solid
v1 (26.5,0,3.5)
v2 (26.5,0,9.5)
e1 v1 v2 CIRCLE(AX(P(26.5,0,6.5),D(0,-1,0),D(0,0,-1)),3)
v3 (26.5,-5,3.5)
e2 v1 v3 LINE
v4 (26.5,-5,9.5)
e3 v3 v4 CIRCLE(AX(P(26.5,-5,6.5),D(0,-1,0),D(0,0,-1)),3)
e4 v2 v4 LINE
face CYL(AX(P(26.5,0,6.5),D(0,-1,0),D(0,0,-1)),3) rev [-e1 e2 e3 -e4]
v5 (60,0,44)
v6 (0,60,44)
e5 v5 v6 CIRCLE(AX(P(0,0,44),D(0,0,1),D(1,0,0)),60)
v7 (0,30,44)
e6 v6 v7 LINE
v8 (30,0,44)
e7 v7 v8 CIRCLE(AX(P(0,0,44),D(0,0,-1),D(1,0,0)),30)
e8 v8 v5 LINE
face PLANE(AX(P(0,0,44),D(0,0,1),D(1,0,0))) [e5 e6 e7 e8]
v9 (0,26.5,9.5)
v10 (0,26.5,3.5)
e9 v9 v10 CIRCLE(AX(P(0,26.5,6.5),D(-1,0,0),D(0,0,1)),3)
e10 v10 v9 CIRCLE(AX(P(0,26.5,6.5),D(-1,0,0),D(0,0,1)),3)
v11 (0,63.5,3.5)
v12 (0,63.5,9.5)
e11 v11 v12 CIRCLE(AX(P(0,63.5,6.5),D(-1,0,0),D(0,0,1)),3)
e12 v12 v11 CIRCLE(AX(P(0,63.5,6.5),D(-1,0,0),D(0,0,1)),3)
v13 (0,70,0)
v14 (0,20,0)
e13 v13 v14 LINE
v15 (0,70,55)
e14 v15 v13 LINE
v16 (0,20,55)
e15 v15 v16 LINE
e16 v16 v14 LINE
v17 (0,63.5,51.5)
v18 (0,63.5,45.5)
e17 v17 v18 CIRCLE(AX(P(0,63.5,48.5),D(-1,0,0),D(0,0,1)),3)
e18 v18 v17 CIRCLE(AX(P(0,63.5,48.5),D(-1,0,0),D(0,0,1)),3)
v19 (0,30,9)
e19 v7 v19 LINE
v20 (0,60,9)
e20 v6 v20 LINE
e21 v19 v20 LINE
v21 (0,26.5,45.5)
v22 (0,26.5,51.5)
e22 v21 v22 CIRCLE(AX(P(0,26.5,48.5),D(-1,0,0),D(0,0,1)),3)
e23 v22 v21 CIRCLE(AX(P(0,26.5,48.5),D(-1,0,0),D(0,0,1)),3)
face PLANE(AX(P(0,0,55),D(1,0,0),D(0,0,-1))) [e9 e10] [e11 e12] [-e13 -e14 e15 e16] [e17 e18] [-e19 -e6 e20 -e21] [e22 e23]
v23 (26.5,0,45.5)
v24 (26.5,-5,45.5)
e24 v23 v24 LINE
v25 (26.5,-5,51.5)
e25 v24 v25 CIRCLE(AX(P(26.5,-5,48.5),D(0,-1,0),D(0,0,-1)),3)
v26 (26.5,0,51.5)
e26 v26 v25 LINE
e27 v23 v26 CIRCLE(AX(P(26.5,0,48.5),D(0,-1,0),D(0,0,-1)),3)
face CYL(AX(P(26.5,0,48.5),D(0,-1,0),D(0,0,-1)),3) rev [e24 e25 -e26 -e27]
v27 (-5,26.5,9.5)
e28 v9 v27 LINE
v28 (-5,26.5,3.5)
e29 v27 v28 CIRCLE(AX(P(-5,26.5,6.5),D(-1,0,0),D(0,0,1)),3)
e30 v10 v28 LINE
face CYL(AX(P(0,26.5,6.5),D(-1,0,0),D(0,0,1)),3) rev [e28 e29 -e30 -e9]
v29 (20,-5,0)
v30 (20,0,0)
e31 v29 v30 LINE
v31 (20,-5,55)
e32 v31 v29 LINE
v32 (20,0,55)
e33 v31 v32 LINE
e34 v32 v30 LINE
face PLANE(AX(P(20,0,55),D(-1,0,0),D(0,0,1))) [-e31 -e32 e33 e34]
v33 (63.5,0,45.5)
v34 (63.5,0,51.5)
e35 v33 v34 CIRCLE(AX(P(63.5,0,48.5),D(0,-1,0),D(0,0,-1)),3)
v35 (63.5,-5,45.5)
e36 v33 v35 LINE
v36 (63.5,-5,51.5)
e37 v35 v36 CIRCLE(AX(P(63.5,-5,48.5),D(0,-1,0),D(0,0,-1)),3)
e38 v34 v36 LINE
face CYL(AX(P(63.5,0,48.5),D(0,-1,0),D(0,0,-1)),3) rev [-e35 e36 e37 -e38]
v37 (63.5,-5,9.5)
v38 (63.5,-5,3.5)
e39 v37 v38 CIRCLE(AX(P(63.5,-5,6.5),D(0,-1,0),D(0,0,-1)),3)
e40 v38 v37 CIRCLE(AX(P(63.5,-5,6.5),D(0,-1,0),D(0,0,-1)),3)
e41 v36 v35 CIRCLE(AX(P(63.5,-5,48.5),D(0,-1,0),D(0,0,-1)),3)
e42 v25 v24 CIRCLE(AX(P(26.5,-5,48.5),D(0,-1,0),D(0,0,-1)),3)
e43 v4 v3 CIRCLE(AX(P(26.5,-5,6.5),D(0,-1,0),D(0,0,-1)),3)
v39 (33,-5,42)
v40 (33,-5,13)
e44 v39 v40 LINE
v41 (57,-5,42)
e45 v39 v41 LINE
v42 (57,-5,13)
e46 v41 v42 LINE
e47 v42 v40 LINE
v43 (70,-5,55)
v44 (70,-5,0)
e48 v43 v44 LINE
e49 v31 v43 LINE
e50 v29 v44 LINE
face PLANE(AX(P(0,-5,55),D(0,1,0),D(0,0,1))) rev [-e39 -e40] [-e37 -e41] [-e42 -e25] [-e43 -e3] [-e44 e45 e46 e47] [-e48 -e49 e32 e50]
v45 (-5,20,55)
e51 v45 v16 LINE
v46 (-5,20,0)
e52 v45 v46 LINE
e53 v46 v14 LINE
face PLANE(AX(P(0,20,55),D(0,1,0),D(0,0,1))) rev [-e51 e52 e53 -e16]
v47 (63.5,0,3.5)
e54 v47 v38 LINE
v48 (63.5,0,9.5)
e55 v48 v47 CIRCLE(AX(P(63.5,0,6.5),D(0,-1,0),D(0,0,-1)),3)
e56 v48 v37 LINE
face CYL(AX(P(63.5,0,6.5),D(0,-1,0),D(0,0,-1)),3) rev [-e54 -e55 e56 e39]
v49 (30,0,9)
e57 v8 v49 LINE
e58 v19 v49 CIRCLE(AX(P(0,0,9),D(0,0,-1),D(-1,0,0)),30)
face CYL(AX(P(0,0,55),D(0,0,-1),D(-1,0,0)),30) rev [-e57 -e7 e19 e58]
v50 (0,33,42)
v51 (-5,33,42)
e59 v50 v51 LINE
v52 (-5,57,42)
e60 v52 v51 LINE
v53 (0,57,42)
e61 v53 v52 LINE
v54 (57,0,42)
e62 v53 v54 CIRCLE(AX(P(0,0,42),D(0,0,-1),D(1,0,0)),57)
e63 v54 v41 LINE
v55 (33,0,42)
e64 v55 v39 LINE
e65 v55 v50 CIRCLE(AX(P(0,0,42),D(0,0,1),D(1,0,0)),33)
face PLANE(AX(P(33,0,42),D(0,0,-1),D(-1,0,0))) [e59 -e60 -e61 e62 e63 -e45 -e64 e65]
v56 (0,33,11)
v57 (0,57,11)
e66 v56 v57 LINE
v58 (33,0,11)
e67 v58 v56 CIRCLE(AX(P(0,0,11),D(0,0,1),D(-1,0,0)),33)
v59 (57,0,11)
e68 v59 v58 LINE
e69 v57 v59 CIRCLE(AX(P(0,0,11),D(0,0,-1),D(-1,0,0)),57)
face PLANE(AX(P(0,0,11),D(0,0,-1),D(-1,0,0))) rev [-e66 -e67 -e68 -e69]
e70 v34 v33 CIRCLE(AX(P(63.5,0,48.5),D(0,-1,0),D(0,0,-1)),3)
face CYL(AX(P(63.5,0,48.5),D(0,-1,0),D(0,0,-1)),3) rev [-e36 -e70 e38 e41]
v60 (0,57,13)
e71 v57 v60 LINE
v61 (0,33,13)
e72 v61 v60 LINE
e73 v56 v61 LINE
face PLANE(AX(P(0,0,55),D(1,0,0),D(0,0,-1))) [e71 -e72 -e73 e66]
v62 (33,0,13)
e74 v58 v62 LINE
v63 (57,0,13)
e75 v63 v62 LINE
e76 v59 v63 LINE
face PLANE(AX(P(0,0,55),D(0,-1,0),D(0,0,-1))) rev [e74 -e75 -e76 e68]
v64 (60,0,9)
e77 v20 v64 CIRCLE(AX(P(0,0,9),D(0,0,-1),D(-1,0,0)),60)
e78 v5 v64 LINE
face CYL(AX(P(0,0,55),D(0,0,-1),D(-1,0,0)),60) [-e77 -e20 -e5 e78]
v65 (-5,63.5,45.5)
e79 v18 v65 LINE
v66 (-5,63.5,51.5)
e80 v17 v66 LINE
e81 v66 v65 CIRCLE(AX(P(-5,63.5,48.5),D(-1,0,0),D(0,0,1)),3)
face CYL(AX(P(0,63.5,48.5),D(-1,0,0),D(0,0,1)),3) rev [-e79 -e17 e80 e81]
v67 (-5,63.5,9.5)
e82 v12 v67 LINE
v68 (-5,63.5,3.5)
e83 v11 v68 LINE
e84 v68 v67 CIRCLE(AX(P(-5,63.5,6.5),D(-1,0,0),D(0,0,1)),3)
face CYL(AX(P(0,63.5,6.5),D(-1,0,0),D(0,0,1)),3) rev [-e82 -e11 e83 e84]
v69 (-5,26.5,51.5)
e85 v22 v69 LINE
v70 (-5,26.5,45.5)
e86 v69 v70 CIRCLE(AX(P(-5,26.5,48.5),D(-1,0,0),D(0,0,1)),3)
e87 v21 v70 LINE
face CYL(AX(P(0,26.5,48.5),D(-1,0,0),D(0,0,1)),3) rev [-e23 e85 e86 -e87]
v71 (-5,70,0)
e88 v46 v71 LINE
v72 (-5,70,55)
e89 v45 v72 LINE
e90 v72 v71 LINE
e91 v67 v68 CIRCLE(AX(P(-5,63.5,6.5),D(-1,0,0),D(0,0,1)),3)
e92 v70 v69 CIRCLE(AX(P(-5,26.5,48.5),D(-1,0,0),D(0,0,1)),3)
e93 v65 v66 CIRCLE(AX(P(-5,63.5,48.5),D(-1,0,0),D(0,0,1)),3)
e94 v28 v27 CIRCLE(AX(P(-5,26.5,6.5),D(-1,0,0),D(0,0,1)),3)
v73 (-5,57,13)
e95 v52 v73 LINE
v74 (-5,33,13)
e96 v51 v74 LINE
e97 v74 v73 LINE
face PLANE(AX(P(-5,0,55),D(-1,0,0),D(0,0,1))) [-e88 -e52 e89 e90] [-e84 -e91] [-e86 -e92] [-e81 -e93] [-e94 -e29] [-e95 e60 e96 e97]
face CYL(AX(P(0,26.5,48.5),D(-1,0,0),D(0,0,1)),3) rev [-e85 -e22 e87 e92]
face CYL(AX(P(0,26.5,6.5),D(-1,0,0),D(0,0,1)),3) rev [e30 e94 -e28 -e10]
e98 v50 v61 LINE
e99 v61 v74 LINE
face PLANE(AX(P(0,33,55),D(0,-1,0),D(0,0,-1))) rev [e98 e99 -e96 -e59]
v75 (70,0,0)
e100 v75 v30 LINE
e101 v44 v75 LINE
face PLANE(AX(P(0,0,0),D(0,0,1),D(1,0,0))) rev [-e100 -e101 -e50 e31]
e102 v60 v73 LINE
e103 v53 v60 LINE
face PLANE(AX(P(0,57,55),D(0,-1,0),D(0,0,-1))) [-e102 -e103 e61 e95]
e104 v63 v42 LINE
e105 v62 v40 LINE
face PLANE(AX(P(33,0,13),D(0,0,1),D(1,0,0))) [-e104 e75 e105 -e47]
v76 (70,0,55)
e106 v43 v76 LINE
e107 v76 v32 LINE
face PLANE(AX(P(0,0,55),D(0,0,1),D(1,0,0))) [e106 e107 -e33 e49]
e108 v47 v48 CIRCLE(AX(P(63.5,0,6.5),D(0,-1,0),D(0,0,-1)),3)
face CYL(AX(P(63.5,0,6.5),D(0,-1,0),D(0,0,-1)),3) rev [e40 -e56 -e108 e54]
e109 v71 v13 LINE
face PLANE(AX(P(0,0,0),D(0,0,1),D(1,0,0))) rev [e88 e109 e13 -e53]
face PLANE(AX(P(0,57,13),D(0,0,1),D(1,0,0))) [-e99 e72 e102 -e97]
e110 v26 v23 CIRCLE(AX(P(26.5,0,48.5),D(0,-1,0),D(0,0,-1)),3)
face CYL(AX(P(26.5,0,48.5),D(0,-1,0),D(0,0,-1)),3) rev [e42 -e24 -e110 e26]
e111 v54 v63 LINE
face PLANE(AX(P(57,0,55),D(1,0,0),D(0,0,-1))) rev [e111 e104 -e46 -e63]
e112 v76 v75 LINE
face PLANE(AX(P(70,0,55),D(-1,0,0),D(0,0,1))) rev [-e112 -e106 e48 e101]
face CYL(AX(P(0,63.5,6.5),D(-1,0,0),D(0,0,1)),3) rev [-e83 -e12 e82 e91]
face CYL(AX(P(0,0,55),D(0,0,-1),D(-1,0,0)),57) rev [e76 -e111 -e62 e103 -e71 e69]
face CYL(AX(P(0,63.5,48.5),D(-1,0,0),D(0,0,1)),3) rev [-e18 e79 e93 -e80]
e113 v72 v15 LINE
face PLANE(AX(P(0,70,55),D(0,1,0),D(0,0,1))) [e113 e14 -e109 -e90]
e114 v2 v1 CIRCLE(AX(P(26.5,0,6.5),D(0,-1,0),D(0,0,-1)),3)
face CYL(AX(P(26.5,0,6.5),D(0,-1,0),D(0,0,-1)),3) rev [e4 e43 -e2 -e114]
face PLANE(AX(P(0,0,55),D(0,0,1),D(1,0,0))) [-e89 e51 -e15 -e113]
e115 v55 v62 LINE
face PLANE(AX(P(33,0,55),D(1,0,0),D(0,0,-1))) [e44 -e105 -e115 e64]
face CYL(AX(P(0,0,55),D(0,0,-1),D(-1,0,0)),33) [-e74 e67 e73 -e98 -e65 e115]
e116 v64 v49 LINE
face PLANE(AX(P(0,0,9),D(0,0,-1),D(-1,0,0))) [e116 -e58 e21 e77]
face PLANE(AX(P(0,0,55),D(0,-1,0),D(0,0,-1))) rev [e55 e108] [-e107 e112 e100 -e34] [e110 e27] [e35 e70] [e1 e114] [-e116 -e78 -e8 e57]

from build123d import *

# Parameters (mm, degrees)
BEND_BODY_DEPTH               = 55
BEND_BODY_2_DEPTH             = 55
FLANGE_A_SKETCH_W             = 24
FLANGE_A_SKETCH_H             = 13
FLANGE_A_DEPTH                = 5
FLANGE_B_SKETCH_W             = 13
FLANGE_B_SKETCH_H             = 24
FLANGE_B_DEPTH                = 5
FLANGE_START                  = -15
FLANGE_B_TRANSITION_CUT_DEPTH = 15
FLANGE_A_TRANSITION_CUT_DEPTH = 15
FLANGE_START_2                = 2
FLANGE_A_PAD_1_DEPTH          = 2
FLANGE_B_PAD_1_DEPTH          = 2
FLANGE_B_PAD_2_DEPTH          = 2
FLANGE_START_3                = -2
FLANGE_B_PAD_3_DEPTH          = 2
FLANGE_A_PAD_2_DEPTH          = 2
FLANGE_A_PAD_3_DEPTH          = 2
FLANGE_A_PAD_4_DEPTH          = 2
BOLT_HOLES_SET_1_SKETCH_R     = 3
BOLT_HOLES_SET_1_4X_DEPTH     = 5
BOLT_HOLES_SET_2_SKETCH_R     = 3
BOLT_HOLES_SET_2_4X_DEPTH     = 5


with BuildPart() as part:
    # Bend Profile Sketch → Bend Body (new body)
    with BuildSketch(Plane.XY):
        with BuildLine():
            Line((0, 57), (-5, 57))
            Line((-5, 57), (-5, 70))
            Line((-5, 70), (0, 70))
            Line((0, 70), (0, 60))
            ThreePointArc((0, 60), (42.426406871, 42.426406871), (60, 0))
            Line((60, 0), (70, 0))
            Line((70, 0), (70, -5))
            Line((70, -5), (57, -5))
            Line((57, -5), (57, 0))
            ThreePointArc((57, 0), (40.305086528, 40.305086528), (0, 57))
        make_face()
    extrude(amount=BEND_BODY_DEPTH)



with BuildPart() as body_2:
    # Bend Profile Sketch → Bend Body 2 (new body)
    with BuildSketch(Plane.XY):
        with BuildLine():
            Line((0, 33), (-5, 33))
            Line((-5, 33), (-5, 20))
            Line((-5, 20), (0, 20))
            Line((0, 20), (0, 30))
            ThreePointArc((0, 30), (21.213203436, 21.213203436), (30, 0))
            Line((30, 0), (20, 0))
            Line((20, 0), (20, -5))
            Line((20, -5), (33, -5))
            Line((33, -5), (33, 0))
            ThreePointArc((33, 0), (23.334523779, 23.334523779), (0, 33))
        make_face()
    extrude(amount=BEND_BODY_2_DEPTH)


with BuildPart() as part_1:
    add(part.part)

    add(body_2.part)  # Flange A merges body 2
    # Flange A Sketch → Flange A (add)
    with BuildSketch(Plane(origin=(0, -5, 0), x_dir=(-1, 0, 0), z_dir=(0, -1, 0))):
        with Locations((-45, -48.5)):
            Rectangle(FLANGE_A_SKETCH_W, FLANGE_A_SKETCH_H)
        with Locations((-45, -6.5)):
            Rectangle(FLANGE_A_SKETCH_W, FLANGE_A_SKETCH_H)
    extrude(amount=-FLANGE_A_DEPTH)

    # Flange B Sketch → Flange B (add)
    with BuildSketch(Plane.ZY.offset(5)):
        with Locations((48.5, 45)):
            Rectangle(FLANGE_B_SKETCH_W, FLANGE_B_SKETCH_H)
        with Locations((6.5, 45)):
            Rectangle(FLANGE_B_SKETCH_W, FLANGE_B_SKETCH_H)
    extrude(amount=-FLANGE_B_DEPTH)

    # Flange B Transition Cut Sketch → Flange B Transition Cut (cut)
    with BuildSketch(Plane.XY.offset(55).offset(FLANGE_START)):
        with BuildLine():
            Line((57, 0), (60, 0))
            ThreePointArc((60, 0), (42.426406871, 42.426406871), (0, 60))
            Line((0, 60), (0, 57))
            ThreePointArc((0, 57), (40.305086528, 40.305086528), (57, 0))
        make_face()
        with BuildLine():
            Line((30, 0), (33, 0))
            ThreePointArc((33, 0), (23.334523779, 23.334523779), (0, 33))
            Line((0, 33), (0, 30))
            ThreePointArc((0, 30), (21.213203436, 21.213203436), (30, 0))
        make_face()
    extrude(amount=FLANGE_B_TRANSITION_CUT_DEPTH, mode=Mode.SUBTRACT)

    # Flange A Transition Cut Sketch → Flange A Transition Cut (cut)
    with BuildSketch(Plane(origin=(0, 0, 0), x_dir=(-1, 0, 0), z_dir=(0, 0, -1))):
        with BuildLine():
            Line((0, 57), (0, 60))
            ThreePointArc((0, 60), (-42.426406871, 42.426406871), (-60, 0))
            Line((-60, 0), (-57, 0))
            ThreePointArc((-57, 0), (-40.305086528, 40.305086528), (0, 57))
        make_face()
        with BuildLine():
            Line((0, 30), (0, 33))
            ThreePointArc((0, 33), (-23.334523779, 23.334523779), (-33, 0))
            Line((-33, 0), (-30, 0))
            ThreePointArc((-30, 0), (-21.213203436, 21.213203436), (0, 30))
        make_face()
    extrude(amount=-FLANGE_A_TRANSITION_CUT_DEPTH, mode=Mode.SUBTRACT)

    # Flange A Pad 1 Sketch → Flange A Pad 1 (add)
    with BuildSketch(Plane(origin=(0, 0, 15), x_dir=(-1, 0, 0), z_dir=(0, 0, -1)).offset(FLANGE_START_2)):
        with BuildLine():
            Line((0, 60), (0, 57))
            ThreePointArc((0, 57), (-40.305086528, 40.305086528), (-57, 0))
            Line((-57, 0), (-60, 0))
            ThreePointArc((-60, 0), (-42.426406871, 42.426406871), (0, 60))
        make_face()
        with BuildLine():
            Line((-33, 0), (-30, 0))
            ThreePointArc((-30, 0), (-21.213203436, 21.213203436), (0, 30))
            Line((0, 30), (0, 33))
            ThreePointArc((0, 33), (-23.334523779, 23.334523779), (-33, 0))
        make_face()
    extrude(amount=-FLANGE_A_PAD_1_DEPTH)

    # Flange B Pad 1 Sketch → Flange B Pad 1 (add)
    with BuildSketch(Plane.XY.offset(40)):
        with BuildLine():
            Line((0, 60), (0, 57))
            ThreePointArc((0, 57), (40.305086528, 40.305086528), (57, 0))
            Line((57, 0), (60, 0))
            ThreePointArc((60, 0), (42.426406871, 42.426406871), (0, 60))
        make_face()
        with BuildLine():
            Line((30, 0), (33, 0))
            ThreePointArc((33, 0), (23.334523779, 23.334523779), (0, 33))
            Line((0, 33), (0, 30))
            ThreePointArc((0, 30), (21.213203436, 21.213203436), (30, 0))
        make_face()
    extrude(amount=FLANGE_B_PAD_1_DEPTH)

    # Flange B Pad 2 Sketch → Flange B Pad 2 (add)
    with BuildSketch(Plane.XY.offset(42)):
        with BuildLine():
            Line((0, 60), (0, 57))
            ThreePointArc((0, 57), (40.305086528, 40.305086528), (57, 0))
            Line((57, 0), (60, 0))
            ThreePointArc((60, 0), (42.426406871, 42.426406871), (0, 60))
        make_face()
        with BuildLine():
            ThreePointArc((33, 0), (23.334523779, 23.334523779), (0, 33))
            Line((0, 33), (0, 30))
            ThreePointArc((0, 30), (21.213203436, 21.213203436), (30, 0))
            Line((30, 0), (33, 0))
        make_face()
    extrude(amount=FLANGE_B_PAD_2_DEPTH)

    # Flange B Pad 3 Sketch → Flange B Pad 3 (add)
    with BuildSketch(Plane.XY.offset(44).offset(FLANGE_START_3)):
        with BuildLine():
            ThreePointArc((57, 0), (40.305086528, 40.305086528), (0, 57))
            Line((0, 57), (0, 33))
            ThreePointArc((0, 33), (23.334523779, 23.334523779), (33, 0))
            Line((33, 0), (57, 0))
        make_face()
    extrude(amount=FLANGE_B_PAD_3_DEPTH)

    # Flange A Pad 2 Sketch → Flange A Pad 2 (add)
    with BuildSketch(Plane(origin=(0, 0, 13), x_dir=(-1, 0, 0), z_dir=(0, 0, -1)).offset(FLANGE_START_2)):
        with BuildLine():
            Line((0, 57), (0, 60))
            ThreePointArc((0, 60), (-42.426406871, 42.426406871), (-60, 0))
            Line((-60, 0), (-57, 0))
            ThreePointArc((-57, 0), (-40.305086528, 40.305086528), (0, 57))
        make_face()
        with BuildLine():
            Line((0, 30), (0, 33))
            ThreePointArc((0, 33), (-23.334523779, 23.334523779), (-33, 0))
            Line((-33, 0), (-30, 0))
            ThreePointArc((-30, 0), (-21.213203436, 21.213203436), (0, 30))
        make_face()
    extrude(amount=-FLANGE_A_PAD_2_DEPTH)

    # Flange A Pad 3 Sketch → Flange A Pad 3 (add)
    with BuildSketch(Plane(origin=(0, 0, 11), x_dir=(-1, 0, 0), z_dir=(0, 0, -1)).offset(FLANGE_START_2)):
        with BuildLine():
            Line((0, 57), (0, 60))
            ThreePointArc((0, 60), (-42.426406871, 42.426406871), (-60, 0))
            Line((-60, 0), (-57, 0))
            ThreePointArc((-57, 0), (-40.305086528, 40.305086528), (0, 57))
        make_face()
        with BuildLine():
            Line((0, 30), (0, 33))
            ThreePointArc((0, 33), (-23.334523779, 23.334523779), (-33, 0))
            Line((-33, 0), (-30, 0))
            ThreePointArc((-30, 0), (-21.213203436, 21.213203436), (0, 30))
        make_face()
    extrude(amount=-FLANGE_A_PAD_3_DEPTH)

    # Flange A Pad 4 Sketch → Flange A Pad 4 (add)
    with BuildSketch(Plane(origin=(0, 0, 9), x_dir=(-1, 0, 0), z_dir=(0, 0, -1))):
        with BuildLine():
            Line((-57, 0), (-33, 0))
            ThreePointArc((-33, 0), (-23.334523779, 23.334523779), (0, 33))
            Line((0, 33), (0, 57))
            ThreePointArc((0, 57), (-40.305086528, 40.305086528), (-57, 0))
        make_face()
    extrude(amount=-FLANGE_A_PAD_4_DEPTH)

    # Bolt Holes Set 1 Sketch → Bolt Holes Set 1 4x (cut)
    with BuildSketch(Plane.ZY.offset(5)):
        with Locations((6.5, 63.5)):
            Circle(BOLT_HOLES_SET_1_SKETCH_R)
        with Locations((48.5, 63.5)):
            Circle(BOLT_HOLES_SET_1_SKETCH_R)
        with Locations((48.5, 26.5)):
            Circle(BOLT_HOLES_SET_1_SKETCH_R)
        with Locations((6.5, 26.5)):
            Circle(BOLT_HOLES_SET_1_SKETCH_R)
    extrude(amount=-BOLT_HOLES_SET_1_4X_DEPTH, mode=Mode.SUBTRACT)

    # Bolt Holes Set 2 Sketch → Bolt Holes Set 2 4x (cut)
    with BuildSketch(Plane.XZ.offset(5)):
        with Locations(Location((26.5, 48.5, 0), (0, 0, 270))):
            Circle(BOLT_HOLES_SET_2_SKETCH_R)
        with Locations(Location((63.5, 48.5, 0), (0, 0, 270))):
            Circle(BOLT_HOLES_SET_2_SKETCH_R)
        with Locations(Location((63.5, 6.5, 0), (0, 0, 270))):
            Circle(BOLT_HOLES_SET_2_SKETCH_R)
        with Locations(Location((26.5, 6.5, 0), (0, 0, 270))):
            Circle(BOLT_HOLES_SET_2_SKETCH_R)
    extrude(amount=-BOLT_HOLES_SET_2_4X_DEPTH, mode=Mode.SUBTRACT)


solid = part_1.part
